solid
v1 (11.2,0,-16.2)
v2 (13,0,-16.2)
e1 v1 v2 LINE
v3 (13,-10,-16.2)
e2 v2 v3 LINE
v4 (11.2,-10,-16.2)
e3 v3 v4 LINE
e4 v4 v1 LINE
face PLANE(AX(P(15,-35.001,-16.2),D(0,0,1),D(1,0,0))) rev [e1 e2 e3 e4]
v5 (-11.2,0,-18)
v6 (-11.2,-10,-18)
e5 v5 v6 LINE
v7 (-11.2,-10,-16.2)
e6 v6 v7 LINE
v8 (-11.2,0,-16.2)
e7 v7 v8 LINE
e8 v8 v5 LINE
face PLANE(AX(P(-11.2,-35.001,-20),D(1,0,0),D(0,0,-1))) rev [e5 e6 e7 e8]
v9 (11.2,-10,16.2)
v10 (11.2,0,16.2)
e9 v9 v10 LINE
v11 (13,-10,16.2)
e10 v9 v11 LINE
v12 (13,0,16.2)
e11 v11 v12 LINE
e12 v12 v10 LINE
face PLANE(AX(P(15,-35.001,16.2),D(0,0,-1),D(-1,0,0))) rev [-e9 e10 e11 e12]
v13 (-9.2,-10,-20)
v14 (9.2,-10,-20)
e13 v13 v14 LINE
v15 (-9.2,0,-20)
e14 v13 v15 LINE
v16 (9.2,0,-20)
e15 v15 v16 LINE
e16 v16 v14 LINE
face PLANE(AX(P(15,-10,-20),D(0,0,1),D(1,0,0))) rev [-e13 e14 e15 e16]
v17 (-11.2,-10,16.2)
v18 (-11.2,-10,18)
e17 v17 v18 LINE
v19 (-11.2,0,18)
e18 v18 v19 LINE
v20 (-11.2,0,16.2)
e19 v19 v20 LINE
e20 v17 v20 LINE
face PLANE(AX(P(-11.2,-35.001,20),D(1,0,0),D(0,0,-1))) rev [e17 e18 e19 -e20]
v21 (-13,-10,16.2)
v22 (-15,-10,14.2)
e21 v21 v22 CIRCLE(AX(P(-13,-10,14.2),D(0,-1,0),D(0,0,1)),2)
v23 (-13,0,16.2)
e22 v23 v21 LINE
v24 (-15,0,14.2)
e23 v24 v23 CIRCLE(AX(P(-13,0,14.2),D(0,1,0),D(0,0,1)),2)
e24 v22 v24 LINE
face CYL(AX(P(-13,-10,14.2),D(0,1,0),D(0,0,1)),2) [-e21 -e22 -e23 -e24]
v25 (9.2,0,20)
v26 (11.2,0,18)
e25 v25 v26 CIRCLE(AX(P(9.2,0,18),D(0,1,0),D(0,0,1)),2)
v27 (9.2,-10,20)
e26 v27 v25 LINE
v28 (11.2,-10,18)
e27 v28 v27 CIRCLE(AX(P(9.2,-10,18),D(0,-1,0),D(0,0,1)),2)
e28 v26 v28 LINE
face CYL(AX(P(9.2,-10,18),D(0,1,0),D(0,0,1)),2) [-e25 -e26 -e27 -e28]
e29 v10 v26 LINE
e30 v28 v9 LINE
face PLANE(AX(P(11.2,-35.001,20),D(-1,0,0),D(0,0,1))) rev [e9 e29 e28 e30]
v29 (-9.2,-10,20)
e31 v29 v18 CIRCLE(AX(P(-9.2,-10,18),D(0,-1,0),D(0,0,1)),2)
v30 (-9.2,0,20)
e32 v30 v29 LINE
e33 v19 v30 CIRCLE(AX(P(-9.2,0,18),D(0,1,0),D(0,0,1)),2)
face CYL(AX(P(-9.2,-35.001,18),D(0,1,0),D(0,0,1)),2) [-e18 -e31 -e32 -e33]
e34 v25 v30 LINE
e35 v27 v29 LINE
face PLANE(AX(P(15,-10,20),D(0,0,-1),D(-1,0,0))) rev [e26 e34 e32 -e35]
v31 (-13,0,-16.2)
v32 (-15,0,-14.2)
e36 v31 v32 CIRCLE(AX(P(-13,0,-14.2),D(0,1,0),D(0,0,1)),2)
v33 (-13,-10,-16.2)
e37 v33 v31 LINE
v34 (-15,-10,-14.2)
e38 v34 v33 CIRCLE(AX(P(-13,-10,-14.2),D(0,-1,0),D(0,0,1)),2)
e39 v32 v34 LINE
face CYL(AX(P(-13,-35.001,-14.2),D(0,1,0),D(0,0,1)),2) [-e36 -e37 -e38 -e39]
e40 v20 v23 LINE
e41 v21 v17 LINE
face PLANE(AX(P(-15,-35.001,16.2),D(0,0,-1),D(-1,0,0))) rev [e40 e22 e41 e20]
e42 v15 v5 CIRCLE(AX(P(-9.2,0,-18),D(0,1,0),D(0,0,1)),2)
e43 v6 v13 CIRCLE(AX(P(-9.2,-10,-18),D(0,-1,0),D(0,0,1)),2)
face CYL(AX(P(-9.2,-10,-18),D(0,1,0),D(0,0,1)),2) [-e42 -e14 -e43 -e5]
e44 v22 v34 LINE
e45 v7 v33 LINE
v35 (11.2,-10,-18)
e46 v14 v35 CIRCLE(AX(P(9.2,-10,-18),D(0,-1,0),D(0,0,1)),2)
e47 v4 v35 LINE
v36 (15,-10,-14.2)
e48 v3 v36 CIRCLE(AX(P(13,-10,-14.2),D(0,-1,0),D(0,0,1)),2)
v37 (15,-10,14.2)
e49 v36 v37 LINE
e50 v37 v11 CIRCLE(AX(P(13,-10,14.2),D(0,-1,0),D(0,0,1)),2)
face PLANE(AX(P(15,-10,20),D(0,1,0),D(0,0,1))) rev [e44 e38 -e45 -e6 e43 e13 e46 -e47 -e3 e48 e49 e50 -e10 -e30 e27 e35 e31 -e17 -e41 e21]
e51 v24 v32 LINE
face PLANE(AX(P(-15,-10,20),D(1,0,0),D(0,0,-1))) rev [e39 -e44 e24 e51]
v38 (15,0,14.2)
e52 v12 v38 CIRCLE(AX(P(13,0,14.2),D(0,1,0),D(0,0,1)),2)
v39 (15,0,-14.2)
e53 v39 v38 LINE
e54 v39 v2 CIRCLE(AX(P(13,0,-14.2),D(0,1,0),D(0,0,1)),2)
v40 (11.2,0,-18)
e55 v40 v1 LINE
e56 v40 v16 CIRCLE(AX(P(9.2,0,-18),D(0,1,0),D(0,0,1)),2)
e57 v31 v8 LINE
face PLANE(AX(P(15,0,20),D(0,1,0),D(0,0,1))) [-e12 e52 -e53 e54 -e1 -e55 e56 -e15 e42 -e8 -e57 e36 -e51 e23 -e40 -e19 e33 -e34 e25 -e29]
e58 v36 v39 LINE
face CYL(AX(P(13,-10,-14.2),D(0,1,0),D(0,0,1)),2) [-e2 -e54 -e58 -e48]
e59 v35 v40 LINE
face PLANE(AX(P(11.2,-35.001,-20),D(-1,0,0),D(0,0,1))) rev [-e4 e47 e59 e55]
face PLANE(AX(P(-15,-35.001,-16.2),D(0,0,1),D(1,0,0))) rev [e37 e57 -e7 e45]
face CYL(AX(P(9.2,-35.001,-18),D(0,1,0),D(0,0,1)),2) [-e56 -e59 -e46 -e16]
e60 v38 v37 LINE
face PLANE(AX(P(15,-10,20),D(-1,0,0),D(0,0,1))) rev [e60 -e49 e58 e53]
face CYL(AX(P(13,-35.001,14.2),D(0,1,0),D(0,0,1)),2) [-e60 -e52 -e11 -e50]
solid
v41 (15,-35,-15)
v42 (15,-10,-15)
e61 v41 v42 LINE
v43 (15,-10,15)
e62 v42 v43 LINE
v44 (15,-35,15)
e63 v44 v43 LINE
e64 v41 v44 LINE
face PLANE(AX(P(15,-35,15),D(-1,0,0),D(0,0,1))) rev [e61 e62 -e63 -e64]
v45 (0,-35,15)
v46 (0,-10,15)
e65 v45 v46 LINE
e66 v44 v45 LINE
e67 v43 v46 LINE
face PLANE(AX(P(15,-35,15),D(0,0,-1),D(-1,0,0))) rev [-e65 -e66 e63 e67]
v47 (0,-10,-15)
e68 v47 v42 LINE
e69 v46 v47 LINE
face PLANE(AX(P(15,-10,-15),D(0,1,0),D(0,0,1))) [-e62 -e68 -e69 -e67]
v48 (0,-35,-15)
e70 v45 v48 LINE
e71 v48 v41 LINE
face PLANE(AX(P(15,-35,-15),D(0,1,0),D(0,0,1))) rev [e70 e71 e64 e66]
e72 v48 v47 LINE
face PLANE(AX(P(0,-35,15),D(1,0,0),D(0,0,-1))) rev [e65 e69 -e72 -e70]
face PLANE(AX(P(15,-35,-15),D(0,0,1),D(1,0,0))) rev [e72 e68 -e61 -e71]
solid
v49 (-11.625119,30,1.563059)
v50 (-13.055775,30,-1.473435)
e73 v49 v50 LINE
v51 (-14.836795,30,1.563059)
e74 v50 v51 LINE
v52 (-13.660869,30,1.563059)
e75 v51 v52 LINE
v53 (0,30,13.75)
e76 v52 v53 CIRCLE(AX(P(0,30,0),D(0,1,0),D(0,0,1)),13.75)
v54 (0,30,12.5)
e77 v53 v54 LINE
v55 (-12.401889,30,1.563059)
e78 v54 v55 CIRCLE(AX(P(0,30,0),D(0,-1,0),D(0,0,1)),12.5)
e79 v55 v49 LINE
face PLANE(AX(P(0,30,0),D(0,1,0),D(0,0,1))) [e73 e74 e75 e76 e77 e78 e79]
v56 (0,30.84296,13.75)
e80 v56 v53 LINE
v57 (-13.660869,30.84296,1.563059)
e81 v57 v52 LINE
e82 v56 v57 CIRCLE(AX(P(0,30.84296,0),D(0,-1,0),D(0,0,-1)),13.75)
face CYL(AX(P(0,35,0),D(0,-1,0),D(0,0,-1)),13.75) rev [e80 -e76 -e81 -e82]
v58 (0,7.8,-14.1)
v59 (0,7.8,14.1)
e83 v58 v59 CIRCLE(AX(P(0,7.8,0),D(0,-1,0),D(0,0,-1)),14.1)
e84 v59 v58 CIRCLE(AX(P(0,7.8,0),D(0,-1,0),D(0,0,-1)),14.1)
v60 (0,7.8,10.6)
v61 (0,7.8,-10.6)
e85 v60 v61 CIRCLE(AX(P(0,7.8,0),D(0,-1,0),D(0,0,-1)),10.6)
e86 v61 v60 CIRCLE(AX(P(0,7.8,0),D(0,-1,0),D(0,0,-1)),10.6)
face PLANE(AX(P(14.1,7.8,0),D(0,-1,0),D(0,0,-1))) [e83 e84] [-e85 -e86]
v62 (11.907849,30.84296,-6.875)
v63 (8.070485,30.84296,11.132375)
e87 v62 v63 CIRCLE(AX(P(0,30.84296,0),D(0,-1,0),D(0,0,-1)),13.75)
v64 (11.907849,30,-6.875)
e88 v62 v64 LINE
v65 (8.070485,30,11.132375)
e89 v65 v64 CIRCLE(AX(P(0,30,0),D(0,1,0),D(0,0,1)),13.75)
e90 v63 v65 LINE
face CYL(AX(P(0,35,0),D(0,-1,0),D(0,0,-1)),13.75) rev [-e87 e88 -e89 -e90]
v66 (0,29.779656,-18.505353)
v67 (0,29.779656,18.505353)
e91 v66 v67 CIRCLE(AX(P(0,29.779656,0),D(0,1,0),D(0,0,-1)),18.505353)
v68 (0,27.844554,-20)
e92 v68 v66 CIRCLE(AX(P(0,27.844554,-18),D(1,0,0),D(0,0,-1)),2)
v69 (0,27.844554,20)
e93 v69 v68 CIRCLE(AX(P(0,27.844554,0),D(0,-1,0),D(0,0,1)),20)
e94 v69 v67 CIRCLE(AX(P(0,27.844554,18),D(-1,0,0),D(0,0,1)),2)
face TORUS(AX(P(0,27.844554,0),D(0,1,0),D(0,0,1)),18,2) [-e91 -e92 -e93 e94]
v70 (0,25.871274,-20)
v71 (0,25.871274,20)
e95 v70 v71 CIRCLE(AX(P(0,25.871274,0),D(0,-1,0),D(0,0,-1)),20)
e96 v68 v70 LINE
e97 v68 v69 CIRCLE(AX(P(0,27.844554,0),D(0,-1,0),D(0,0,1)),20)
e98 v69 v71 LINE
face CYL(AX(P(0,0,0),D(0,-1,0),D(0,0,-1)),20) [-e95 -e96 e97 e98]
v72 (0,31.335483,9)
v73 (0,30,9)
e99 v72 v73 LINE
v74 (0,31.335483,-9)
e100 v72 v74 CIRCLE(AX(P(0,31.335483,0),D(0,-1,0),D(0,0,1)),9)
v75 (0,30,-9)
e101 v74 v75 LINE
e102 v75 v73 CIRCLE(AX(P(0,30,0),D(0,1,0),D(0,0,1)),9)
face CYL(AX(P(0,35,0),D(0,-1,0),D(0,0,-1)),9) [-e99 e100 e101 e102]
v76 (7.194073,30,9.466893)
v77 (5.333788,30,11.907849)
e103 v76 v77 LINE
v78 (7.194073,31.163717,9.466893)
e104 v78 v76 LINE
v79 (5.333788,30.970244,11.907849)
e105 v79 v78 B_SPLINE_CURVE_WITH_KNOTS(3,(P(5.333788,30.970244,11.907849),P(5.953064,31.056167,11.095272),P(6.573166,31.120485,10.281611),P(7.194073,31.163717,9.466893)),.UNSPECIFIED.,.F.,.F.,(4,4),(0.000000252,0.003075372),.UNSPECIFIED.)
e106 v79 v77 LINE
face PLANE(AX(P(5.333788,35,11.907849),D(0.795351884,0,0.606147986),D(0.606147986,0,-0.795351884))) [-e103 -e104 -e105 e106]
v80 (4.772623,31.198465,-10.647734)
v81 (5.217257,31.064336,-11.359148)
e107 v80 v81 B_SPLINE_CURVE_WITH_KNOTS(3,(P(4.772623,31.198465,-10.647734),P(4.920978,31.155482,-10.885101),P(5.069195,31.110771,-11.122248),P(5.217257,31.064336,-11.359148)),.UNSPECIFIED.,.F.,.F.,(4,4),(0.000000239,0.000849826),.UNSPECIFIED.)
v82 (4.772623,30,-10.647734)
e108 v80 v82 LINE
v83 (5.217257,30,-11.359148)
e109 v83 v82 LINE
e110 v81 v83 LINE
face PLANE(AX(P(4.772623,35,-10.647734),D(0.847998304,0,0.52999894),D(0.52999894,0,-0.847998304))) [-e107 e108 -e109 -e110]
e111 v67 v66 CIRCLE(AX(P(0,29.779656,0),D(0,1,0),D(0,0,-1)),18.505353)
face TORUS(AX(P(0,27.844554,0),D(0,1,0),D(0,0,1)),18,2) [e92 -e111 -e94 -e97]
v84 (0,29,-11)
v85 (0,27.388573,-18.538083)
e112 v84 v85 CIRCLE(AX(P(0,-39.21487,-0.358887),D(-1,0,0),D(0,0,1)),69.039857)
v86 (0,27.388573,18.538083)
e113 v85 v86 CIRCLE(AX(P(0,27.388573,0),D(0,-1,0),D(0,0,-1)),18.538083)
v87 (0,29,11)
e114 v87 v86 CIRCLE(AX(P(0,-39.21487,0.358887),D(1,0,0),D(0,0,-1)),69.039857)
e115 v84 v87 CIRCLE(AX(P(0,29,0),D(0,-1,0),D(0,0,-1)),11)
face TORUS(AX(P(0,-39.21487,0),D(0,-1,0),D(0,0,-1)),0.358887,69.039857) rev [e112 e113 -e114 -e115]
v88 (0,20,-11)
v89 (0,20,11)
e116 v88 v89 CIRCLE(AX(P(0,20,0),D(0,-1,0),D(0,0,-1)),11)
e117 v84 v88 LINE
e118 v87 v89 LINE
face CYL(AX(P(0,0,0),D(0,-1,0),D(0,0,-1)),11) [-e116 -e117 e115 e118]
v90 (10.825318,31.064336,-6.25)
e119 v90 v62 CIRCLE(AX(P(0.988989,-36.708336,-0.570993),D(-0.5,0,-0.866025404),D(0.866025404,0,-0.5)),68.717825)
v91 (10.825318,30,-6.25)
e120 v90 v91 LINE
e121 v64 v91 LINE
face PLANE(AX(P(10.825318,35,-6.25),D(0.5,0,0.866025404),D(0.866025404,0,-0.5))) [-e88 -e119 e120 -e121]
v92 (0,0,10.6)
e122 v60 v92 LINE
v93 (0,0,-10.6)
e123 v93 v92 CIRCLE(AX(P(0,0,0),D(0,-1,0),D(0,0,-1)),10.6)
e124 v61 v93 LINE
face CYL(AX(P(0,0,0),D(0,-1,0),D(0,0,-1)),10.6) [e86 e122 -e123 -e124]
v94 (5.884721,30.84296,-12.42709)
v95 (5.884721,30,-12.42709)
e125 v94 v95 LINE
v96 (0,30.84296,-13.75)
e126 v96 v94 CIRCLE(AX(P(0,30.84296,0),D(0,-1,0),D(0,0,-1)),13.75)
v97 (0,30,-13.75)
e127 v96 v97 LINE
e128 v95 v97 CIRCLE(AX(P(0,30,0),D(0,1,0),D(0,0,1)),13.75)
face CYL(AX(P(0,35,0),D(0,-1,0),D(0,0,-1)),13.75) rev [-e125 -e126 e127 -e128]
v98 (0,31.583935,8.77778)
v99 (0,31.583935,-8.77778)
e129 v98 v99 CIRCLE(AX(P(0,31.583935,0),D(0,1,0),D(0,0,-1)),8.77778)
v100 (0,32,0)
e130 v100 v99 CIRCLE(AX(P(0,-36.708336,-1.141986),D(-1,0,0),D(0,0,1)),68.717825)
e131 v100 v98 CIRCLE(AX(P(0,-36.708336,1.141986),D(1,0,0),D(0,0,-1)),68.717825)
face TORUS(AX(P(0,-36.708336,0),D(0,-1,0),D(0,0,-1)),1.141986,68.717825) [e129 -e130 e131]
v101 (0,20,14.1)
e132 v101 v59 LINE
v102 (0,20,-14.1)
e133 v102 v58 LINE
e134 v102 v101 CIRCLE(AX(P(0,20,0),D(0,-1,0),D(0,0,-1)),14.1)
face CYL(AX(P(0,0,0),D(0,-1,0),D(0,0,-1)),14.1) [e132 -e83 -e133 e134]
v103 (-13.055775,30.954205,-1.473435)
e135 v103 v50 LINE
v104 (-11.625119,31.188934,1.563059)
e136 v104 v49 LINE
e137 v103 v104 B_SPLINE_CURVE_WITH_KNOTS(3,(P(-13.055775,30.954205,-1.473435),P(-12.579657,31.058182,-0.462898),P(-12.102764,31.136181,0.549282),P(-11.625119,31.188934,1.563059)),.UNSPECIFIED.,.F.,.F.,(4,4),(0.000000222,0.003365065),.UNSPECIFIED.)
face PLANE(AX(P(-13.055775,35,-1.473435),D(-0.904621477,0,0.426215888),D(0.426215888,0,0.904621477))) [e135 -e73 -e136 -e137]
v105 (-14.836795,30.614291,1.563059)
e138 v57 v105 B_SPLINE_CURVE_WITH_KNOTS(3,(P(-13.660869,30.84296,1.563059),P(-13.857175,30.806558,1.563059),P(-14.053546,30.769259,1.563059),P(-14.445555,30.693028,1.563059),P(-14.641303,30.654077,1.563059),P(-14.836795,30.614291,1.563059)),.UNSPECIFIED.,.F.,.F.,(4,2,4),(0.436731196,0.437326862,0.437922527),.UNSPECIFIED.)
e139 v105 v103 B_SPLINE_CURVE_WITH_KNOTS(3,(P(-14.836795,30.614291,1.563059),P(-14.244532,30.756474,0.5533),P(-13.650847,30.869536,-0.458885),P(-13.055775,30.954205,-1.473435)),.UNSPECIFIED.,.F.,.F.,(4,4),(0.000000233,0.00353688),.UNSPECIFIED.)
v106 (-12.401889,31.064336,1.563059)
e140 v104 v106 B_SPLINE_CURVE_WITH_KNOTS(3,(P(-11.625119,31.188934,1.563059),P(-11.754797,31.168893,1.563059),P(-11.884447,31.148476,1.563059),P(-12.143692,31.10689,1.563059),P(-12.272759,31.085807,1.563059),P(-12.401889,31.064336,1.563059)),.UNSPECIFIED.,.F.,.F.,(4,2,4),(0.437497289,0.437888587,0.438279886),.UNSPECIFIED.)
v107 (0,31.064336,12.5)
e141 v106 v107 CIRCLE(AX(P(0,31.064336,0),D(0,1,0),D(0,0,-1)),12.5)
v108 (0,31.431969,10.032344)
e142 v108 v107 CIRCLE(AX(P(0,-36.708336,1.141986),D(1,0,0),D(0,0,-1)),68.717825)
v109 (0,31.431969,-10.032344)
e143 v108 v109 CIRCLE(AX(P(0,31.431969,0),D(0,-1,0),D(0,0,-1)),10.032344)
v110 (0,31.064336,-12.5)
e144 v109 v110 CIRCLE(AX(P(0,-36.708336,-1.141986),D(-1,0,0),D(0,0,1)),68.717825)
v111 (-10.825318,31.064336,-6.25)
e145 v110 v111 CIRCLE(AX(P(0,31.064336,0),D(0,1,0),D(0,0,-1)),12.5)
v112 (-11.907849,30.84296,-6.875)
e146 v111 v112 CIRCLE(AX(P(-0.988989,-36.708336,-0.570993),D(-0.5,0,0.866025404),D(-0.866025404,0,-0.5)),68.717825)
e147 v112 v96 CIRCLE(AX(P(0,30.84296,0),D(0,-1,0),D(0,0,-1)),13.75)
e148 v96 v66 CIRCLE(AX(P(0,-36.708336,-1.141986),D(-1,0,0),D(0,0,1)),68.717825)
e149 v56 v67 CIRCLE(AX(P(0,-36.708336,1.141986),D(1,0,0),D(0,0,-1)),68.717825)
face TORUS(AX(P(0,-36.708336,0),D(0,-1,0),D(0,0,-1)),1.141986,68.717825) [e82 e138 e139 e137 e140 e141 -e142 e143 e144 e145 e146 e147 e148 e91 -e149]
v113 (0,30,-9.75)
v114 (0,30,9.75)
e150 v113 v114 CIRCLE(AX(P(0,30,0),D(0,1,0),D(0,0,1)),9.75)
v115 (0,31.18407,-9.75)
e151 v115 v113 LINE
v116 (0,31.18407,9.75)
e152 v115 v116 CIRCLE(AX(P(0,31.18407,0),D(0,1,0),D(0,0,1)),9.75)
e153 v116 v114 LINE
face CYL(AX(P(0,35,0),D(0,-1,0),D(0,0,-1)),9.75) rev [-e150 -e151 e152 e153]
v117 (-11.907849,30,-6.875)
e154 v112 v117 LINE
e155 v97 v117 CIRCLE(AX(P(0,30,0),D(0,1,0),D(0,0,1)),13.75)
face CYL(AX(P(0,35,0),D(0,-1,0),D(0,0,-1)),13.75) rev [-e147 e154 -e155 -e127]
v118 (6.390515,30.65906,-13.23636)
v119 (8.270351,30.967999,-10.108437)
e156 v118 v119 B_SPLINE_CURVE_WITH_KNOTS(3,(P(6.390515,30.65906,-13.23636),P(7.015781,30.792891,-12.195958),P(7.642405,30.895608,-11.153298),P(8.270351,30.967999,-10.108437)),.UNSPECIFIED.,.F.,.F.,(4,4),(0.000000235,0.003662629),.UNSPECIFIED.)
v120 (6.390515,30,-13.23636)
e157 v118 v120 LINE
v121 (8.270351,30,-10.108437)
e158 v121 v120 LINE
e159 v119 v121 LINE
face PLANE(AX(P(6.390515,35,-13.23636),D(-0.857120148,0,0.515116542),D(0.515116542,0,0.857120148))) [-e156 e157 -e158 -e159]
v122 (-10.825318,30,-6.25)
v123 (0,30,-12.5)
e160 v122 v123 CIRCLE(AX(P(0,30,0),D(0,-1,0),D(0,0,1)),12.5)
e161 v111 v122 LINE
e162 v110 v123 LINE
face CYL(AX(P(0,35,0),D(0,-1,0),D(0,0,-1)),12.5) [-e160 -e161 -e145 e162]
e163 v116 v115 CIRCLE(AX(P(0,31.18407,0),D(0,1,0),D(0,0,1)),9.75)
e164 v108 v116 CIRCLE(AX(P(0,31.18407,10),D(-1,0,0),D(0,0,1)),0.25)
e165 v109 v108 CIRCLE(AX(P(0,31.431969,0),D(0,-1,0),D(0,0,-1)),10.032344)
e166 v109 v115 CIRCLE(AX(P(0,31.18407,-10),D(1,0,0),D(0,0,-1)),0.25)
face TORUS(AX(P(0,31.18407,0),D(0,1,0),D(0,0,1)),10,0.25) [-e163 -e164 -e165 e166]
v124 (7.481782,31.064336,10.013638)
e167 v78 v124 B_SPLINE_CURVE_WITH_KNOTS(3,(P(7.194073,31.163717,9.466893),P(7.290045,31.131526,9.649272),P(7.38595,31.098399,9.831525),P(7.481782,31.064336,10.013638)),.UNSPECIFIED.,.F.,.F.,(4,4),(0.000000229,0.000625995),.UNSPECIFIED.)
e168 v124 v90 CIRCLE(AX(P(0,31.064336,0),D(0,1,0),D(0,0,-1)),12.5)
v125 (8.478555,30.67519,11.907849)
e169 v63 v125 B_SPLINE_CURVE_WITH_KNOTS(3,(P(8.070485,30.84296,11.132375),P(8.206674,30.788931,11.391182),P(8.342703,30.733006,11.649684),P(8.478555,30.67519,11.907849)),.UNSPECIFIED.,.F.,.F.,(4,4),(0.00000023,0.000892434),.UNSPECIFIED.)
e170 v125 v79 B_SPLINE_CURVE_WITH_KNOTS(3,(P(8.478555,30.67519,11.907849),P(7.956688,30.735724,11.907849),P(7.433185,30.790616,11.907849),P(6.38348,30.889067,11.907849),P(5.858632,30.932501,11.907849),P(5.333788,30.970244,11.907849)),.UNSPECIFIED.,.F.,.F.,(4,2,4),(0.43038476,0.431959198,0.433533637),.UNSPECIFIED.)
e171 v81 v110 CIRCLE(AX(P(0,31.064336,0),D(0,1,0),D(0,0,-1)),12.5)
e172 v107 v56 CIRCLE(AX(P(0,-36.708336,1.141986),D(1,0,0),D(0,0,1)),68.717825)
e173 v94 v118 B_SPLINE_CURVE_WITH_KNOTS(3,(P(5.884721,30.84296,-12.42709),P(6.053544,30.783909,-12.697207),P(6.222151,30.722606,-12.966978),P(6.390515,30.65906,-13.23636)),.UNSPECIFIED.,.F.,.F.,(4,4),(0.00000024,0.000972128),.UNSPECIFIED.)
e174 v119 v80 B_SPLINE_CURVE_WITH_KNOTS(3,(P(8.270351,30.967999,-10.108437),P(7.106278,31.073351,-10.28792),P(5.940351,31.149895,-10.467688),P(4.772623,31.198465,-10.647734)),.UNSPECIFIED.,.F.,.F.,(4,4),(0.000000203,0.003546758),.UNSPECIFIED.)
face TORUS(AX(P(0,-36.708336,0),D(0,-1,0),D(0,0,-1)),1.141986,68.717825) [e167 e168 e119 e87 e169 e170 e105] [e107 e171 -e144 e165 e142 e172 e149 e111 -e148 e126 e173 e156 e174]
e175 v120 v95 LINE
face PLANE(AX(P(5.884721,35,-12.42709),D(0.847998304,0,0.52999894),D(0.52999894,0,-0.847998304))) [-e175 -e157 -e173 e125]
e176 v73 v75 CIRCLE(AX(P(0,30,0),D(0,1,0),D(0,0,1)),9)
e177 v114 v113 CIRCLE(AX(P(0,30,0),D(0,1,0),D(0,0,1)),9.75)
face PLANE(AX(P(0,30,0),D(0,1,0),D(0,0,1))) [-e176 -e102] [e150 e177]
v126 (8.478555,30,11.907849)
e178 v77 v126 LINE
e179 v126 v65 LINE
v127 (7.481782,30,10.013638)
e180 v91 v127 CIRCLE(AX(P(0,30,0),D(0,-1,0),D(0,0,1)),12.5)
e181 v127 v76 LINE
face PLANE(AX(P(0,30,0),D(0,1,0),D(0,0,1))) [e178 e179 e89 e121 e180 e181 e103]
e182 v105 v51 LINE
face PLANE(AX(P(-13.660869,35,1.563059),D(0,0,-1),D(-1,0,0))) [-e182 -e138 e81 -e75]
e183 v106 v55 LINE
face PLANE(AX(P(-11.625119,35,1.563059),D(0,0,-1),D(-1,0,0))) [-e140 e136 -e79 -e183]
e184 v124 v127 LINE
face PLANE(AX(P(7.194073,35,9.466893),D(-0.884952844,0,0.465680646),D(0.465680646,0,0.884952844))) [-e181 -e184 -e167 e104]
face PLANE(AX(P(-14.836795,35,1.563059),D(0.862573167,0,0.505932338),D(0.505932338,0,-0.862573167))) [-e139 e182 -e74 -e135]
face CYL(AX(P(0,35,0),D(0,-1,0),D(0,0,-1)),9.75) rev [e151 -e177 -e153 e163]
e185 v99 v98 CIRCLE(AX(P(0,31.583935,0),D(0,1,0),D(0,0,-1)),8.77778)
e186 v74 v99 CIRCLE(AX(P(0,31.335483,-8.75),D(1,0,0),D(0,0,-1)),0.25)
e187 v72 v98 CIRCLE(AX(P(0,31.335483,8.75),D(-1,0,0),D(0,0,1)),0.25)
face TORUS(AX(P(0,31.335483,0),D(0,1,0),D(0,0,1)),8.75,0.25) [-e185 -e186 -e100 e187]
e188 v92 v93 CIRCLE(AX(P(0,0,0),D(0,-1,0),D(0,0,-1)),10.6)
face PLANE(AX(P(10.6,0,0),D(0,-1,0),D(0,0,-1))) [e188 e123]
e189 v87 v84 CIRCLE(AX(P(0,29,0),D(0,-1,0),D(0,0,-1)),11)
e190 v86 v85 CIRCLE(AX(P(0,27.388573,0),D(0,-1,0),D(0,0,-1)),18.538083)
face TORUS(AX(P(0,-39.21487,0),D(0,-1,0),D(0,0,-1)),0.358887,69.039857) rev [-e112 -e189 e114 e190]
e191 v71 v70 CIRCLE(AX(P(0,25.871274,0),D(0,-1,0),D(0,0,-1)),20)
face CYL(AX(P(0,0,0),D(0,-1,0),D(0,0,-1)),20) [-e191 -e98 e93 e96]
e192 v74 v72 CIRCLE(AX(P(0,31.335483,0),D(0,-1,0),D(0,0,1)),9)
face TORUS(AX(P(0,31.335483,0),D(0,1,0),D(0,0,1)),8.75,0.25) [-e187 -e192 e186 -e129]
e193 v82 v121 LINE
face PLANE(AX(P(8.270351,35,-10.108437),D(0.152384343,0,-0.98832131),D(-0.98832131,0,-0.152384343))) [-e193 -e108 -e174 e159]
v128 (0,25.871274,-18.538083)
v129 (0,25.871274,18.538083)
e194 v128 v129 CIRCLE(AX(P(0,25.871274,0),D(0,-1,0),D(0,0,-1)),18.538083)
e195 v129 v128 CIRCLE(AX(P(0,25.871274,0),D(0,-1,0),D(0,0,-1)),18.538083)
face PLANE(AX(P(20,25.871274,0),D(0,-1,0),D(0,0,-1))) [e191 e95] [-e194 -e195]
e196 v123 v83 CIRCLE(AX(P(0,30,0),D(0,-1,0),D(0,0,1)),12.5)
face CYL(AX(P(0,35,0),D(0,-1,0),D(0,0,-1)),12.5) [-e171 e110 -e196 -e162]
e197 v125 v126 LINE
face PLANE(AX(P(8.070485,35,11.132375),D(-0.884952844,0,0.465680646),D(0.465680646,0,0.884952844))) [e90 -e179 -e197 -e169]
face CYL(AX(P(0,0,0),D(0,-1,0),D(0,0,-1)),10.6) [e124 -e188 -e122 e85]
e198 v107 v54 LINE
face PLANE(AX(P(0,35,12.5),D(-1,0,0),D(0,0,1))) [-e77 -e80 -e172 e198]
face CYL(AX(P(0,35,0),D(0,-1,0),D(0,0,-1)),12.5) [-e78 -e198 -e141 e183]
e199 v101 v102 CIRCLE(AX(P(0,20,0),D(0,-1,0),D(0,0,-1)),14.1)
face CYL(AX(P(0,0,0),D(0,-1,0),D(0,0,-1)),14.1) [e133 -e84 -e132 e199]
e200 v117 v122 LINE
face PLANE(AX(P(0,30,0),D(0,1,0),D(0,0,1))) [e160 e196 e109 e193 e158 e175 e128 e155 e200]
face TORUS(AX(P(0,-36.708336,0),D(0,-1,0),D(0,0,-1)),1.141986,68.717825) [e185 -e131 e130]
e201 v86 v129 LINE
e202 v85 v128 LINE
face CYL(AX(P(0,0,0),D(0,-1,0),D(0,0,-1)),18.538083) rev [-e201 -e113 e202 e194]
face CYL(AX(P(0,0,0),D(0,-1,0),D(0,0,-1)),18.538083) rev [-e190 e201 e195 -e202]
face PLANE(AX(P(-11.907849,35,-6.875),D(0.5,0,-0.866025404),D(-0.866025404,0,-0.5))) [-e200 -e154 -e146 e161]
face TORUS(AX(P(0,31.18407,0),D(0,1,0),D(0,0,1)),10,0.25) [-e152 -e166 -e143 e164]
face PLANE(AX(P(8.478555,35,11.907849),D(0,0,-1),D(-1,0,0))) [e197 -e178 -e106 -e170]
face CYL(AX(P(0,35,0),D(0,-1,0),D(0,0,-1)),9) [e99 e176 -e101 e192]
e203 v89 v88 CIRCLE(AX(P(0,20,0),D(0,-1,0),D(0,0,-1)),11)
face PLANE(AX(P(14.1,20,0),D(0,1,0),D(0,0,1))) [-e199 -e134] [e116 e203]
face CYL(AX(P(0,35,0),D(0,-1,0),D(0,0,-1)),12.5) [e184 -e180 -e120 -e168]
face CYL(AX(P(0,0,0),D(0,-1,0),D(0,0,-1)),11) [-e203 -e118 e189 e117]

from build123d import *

# Parameters (mm, degrees)
SKETCH_2_W          = 30
SKETCH_2_H          = 40
EXTRUDE_1_DEPTH     = 10
SKETCH_3_W          = 15
SKETCH_3_H          = 30
EXTRUDE_2_DEPTH     = 25
SKETCH_7_W          = 3.8
SKETCH_7_H          = 3.8
CUT_EXTRUDE_2_DEPTH = 10
FILLET_1_R          = 2
FILLET_2_R          = 2
SKETCH_8_R          = 9.75
SKETCH_8_R_2        = 9
CUT_EXTRUDE_4_DEPTH = 5
CUT_EXTRUDE_5_DEPTH = 5
FILLET_3_R          = 0.25


with BuildPart() as part:
    # 草图1 → 旋转1 (revolve)
    with BuildSketch(Plane.XY, mode=Mode.PRIVATE) as revolve_1_sk:
        with BuildLine():
            Line((14.1, 20), (11, 20))
            Line((11, 20), (11, 29))
            ThreePointArc((11, 29), (14.791548694, 28.29957327), (18.538082764, 27.388572956))
            Line((18.538082764, 27.388572956), (18.538082764, 25.871274116))
            Line((18.538082764, 25.871274116), (20, 25.871274116))
            Line((20, 25.871274116), (20, 29.371274116))
            ThreePointArc((20, 29.371274116), (10.09698248, 31.423503879), (0, 32))
            Line((0, 32), (0, 0))
            Line((0, 0), (10.6, 0))
            Line((10.6, 0), (10.6, 7.8))
            Line((10.6, 7.8), (14.1, 7.8))
            Line((14.1, 7.8), (14.1, 20))
        make_face()
    revolve(revolve_1_sk.sketch.rotate(Axis((0, 0, 0), (0, 1, 0)), 90), axis=Axis((0, 0, 0), (0, 1, 0)))

    # 圆角2
    fillet_2_edges = [part.edges().sort_by_distance(p)[0] for p in [
        (0, 29.371274116, 20),
    ]]
    fillet(fillet_2_edges, radius=FILLET_2_R)

    # 草图8 → 切除-拉伸4 (cut)
    with BuildSketch(Plane(origin=(0, 30, 0), x_dir=(-1, 0, 0), z_dir=(0, 1, 0))):
        with Locations(Location((0, 0, 0), (0, 0, 270))):
            Circle(SKETCH_8_R)
        with Locations(Location((0, 0, 0), (0, 0, 270))):
            Circle(SKETCH_8_R_2, mode=Mode.SUBTRACT)
    extrude(amount=CUT_EXTRUDE_4_DEPTH, mode=Mode.SUBTRACT)

    # 草图9 → 切除-拉伸5 (cut)
    with BuildSketch(Plane(origin=(0, 30, 0), x_dir=(-1, 0, 0), z_dir=(0, 1, 0))):
        with BuildLine():
            Line((11.907849302, -6.875), (10.825317547, -6.25))
            ThreePointArc((10.825317547, -6.25), (3.79320889, -11.910565323), (-5.217256711, -11.359147521))
            Line((-5.217256711, -11.359147521), (-4.772623337, -10.647734123))
            Line((-4.772623337, -10.647734123), (-8.270350551, -10.108436975))
            Line((-8.270350551, -10.108436975), (-6.39051478, -13.236360431))
            Line((-6.39051478, -13.236360431), (-5.884720677, -12.427089867))
            ThreePointArc((-5.884720677, -12.427089867), (4.095844856, -13.125797306), (11.907849302, -6.875))
        make_face()
        with BuildLine():
            Line((0, 12.5), (0, 13.75))
            ThreePointArc((0, 13.75), (9.153426635, 10.260471765), (13.660869169, 1.563059031))
            Line((13.660869169, 1.563059031), (14.836795077, 1.563059031))
            Line((14.836795077, 1.563059031), (13.055774782, -1.473434586))
            Line((13.055774782, -1.473434586), (11.625119135, 1.563059031))
            Line((11.625119135, 1.563059031), (12.401888827, 1.563059031))
            ThreePointArc((12.401888827, 1.563059031), (8.26776155, 9.375186342), (0, 12.5))
        make_face()
        with BuildLine():
            Line((-10.825317547, -6.25), (-11.907849302, -6.875))
            ThreePointArc((-11.907849302, -6.875), (-13.448042492, 2.865772692), (-8.070484546, 11.132375272))
            Line((-8.070484546, 11.132375272), (-8.478555156, 11.907849302))
            Line((-8.478555156, 11.907849302), (-5.333788149, 11.907849302))
            Line((-5.333788149, 11.907849302), (-7.194072858, 9.466892667))
            Line((-7.194072858, 9.466892667), (-7.481781605, 10.013637901))
            ThreePointArc((-7.481781605, 10.013637901), (-12.243935204, 2.517151309), (-10.825317547, -6.25))
        make_face()
    extrude(amount=CUT_EXTRUDE_5_DEPTH, mode=Mode.SUBTRACT)

    # 圆角3
    fillet_3_edges = [part.edges().sort_by_distance(p)[0] for p in [
        (1e-09, 31.468211744, 9.749999987),
        (2e-09, 31.558721819, 9),
    ]]
    fillet(fillet_3_edges, radius=FILLET_3_R)


with BuildPart() as body_2:
    # 草图2 → 拉伸1 (new body)
    with BuildSketch(Plane.XZ):
        Rectangle(SKETCH_2_W, SKETCH_2_H)
    extrude(amount=EXTRUDE_1_DEPTH)

    # 草图7 → 切除-拉伸2 (cut)
    with BuildSketch(Plane(origin=(0, 0, 0), x_dir=(-1, 0, 0), z_dir=(0, 1, 0))):
        with Locations((-13.1, 18.1)):
            Rectangle(SKETCH_7_W, SKETCH_7_H)
        with Locations((13.1, 18.1)):
            Rectangle(SKETCH_7_W, SKETCH_7_H)
        with Locations((13.1, -18.1)):
            Rectangle(SKETCH_7_W, SKETCH_7_H)
        with Locations((-13.1, -18.1)):
            Rectangle(SKETCH_7_W, SKETCH_7_H)
    extrude(amount=-CUT_EXTRUDE_2_DEPTH, mode=Mode.SUBTRACT)

    # 圆角1
    fillet_1_edges = [body_2.edges().sort_by_distance(p)[0] for p in [
        (15, -5, 16.2),
        (11.2, -5, 20),
        (-11.2, -5, 20),
        (-15, -5, 16.2),
        (-15, -5, -16.2),
        (-11.2, -5, -20),
        (11.2, -5, -20),
        (15, -5, -16.2),
    ]]
    fillet(fillet_1_edges, radius=FILLET_1_R)


with BuildPart() as body_3:
    # 草图3 → 拉伸2 (new body)
    with BuildSketch(Plane.XZ.offset(10)):
        with Locations((7.5, 0)):
            Rectangle(SKETCH_3_W, SKETCH_3_H)
    extrude(amount=EXTRUDE_2_DEPTH)


solid = Compound([part.part, body_2.part, body_3.part])
